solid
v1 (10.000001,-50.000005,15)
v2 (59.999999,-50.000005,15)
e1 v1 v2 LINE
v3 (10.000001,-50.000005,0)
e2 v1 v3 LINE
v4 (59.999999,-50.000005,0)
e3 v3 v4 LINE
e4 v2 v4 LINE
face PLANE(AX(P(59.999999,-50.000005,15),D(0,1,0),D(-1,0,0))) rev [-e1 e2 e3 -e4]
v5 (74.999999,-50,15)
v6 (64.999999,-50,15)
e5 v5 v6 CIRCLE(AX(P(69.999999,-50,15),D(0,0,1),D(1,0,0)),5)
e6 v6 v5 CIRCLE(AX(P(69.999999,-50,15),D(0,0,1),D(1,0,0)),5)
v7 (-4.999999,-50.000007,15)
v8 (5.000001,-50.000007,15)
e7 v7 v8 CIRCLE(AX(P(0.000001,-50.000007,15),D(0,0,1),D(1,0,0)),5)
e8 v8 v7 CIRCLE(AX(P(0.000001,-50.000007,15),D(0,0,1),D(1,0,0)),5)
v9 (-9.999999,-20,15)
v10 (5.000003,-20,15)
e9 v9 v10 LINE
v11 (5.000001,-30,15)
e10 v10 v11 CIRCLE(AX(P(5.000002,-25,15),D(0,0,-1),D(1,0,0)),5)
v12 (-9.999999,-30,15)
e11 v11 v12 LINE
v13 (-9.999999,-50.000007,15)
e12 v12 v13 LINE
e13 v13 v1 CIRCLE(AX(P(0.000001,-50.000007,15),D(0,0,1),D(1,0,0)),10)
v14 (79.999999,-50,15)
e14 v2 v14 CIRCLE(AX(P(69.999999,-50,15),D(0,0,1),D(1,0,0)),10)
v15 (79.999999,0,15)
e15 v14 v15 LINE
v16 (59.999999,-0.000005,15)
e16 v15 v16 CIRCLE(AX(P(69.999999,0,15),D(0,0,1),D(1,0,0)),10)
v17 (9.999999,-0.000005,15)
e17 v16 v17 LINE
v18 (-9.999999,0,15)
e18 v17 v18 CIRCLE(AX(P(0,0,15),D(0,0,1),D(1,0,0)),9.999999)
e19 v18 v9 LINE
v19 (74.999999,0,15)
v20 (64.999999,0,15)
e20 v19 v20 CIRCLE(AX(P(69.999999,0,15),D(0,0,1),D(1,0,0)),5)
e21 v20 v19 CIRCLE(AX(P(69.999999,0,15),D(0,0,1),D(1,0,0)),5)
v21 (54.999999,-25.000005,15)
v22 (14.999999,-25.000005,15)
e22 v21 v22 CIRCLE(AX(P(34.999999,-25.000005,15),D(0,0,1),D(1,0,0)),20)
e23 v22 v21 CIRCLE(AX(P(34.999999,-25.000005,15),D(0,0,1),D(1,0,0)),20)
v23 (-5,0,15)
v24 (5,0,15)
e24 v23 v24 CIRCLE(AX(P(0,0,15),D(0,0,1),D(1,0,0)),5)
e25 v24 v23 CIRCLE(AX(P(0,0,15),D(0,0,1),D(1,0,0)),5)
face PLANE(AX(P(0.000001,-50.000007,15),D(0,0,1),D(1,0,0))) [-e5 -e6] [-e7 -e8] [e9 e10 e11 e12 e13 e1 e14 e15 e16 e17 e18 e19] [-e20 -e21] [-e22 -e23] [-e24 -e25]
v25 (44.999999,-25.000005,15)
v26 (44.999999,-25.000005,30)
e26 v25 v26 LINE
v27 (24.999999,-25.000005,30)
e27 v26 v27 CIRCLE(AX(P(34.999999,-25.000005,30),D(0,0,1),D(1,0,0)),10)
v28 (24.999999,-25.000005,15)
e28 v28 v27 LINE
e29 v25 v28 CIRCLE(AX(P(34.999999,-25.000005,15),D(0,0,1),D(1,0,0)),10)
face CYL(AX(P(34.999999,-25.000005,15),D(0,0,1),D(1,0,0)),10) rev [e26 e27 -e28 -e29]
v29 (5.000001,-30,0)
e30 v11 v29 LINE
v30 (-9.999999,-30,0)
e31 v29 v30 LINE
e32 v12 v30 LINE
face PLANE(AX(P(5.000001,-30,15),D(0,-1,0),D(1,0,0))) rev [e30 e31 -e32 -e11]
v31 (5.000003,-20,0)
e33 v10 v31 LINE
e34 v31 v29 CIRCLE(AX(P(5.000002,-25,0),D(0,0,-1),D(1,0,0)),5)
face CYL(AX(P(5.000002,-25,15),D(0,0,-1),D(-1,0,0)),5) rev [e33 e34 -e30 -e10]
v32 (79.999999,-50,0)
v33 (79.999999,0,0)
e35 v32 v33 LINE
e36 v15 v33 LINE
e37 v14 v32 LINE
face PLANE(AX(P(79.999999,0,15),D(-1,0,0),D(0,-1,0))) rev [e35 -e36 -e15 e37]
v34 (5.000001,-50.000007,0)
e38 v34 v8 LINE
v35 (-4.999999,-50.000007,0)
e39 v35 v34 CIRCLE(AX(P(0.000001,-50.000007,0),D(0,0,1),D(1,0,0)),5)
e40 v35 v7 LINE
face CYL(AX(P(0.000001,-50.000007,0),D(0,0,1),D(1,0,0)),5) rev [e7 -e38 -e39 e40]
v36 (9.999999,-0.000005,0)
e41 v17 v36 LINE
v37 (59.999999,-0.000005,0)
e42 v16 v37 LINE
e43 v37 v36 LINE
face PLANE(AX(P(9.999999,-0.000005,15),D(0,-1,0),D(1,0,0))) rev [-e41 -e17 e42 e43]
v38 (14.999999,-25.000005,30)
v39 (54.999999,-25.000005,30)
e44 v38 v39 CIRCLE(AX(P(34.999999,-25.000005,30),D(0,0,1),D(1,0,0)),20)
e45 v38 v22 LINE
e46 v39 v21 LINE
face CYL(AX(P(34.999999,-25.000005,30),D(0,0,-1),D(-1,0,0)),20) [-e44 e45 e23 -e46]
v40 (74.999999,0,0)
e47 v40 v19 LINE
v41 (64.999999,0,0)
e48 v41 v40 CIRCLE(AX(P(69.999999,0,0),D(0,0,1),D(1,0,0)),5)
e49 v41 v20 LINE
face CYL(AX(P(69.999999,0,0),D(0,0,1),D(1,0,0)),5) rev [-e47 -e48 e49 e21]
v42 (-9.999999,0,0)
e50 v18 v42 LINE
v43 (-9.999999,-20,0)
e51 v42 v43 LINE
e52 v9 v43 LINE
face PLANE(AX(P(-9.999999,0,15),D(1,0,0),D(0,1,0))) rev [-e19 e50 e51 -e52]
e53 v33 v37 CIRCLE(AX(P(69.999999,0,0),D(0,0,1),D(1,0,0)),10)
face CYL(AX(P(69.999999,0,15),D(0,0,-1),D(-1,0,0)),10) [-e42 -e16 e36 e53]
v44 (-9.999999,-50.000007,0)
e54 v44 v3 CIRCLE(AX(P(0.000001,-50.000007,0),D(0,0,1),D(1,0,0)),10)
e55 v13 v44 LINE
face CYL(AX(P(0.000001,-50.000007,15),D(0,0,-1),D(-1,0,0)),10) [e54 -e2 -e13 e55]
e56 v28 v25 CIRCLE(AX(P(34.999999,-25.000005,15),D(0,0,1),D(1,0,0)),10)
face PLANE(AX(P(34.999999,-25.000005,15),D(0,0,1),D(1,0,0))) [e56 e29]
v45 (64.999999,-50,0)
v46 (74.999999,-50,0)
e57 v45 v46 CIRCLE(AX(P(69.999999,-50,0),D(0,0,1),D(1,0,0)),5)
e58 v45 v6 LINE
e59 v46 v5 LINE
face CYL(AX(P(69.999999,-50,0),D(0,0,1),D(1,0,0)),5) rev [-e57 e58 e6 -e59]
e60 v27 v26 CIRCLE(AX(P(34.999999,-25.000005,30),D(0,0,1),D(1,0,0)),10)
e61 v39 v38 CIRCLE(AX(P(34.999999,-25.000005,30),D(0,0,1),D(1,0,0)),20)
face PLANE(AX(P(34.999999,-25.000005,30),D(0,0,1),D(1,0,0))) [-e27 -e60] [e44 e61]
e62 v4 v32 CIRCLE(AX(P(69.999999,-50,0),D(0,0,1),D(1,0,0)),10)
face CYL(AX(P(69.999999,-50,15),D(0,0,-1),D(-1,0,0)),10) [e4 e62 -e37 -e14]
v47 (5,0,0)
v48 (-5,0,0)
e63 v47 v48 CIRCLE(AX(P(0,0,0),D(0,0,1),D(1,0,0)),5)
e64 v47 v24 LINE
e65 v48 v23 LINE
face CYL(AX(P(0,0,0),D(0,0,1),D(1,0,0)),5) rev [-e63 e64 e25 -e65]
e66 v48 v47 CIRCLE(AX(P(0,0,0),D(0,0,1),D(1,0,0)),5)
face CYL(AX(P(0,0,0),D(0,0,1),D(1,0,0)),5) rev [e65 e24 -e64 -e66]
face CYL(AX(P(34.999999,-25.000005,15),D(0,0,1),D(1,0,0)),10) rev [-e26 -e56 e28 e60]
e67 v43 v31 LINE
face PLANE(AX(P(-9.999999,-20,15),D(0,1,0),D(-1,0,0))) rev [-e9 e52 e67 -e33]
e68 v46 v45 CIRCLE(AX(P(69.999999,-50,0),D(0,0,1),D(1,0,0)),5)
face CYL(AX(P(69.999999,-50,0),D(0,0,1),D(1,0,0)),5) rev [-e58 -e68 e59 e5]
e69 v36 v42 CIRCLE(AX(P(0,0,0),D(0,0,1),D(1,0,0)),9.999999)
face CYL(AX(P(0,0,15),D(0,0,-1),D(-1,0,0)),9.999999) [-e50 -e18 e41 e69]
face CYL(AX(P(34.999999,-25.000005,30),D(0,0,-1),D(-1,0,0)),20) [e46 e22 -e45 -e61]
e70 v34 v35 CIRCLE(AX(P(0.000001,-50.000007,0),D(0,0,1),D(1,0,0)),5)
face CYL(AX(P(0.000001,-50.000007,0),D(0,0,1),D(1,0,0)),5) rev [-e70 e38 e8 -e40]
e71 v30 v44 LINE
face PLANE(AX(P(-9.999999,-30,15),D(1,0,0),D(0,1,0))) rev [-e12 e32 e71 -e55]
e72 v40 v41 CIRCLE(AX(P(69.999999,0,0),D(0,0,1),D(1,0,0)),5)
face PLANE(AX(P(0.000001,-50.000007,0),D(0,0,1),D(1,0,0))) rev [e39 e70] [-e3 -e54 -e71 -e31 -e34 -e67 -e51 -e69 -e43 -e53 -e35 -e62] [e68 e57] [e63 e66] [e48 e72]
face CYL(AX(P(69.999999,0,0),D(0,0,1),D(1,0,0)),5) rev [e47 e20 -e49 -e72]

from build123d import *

# Parameters (mm, degrees)
FLANGE_PLATE_DEPTH     = 15
SIDE_NOTCH_SKETCH_R    = 5
SIDE_NOTCH_10X10_DEPTH = 15
HUB_BOSS_SKETCH_R      = 20
HUB_BOSS_40_DEPTH      = 15
BORE_SKETCH_R          = 10
BORE_20_DEPTH          = 15


with BuildPart() as part:
    # Flange Plate Profile Sketch → Flange Plate (new body)
    with BuildSketch(Plane.XY):
        with BuildLine():
            Line((9.999999107, -5.133e-06), (59.999999107, -5.133e-06))
            ThreePointArc((59.999999107, -5.133e-06), (69.999996541, 10), (79.999999107, 0))
            Line((79.999999107, 0), (79.999999107, -50))
            ThreePointArc((79.999999107, -50), (70.000001674, -60), (59.999999107, -50.000005133))
            Line((59.999999107, -50.000005133), (10.000000893, -50.000005133))
            ThreePointArc((10.000000893, -50.000005133), (1.674e-06, -60.000006696), (-9.999999107, -50.000006696))
            Line((-9.999999107, -50.000006696), (-9.999999107, -30))
            Line((-9.999999107, -30), (5.000000893, -30))
            ThreePointArc((5.000000893, -30), (10.000001691, -25.000000893), (5.000002678, -20))
            Line((5.000002678, -20), (-9.999999107, -20))
            Line((-9.999999107, -20), (-9.999999107, 0))
            ThreePointArc((-9.999999107, 0), (2.567e-06, 9.999999107), (9.999999107, -5.133e-06))
        make_face()
    extrude(amount=FLANGE_PLATE_DEPTH)

    # Side Notch Sketch → Side Notch 10x10 (cut)
    with BuildSketch(Plane.XY.offset(15)):
        Circle(SIDE_NOTCH_SKETCH_R)
        with Locations((69.999999107, 0)):
            Circle(SIDE_NOTCH_SKETCH_R)
        with Locations((69.999999107, -50)):
            Circle(SIDE_NOTCH_SKETCH_R)
        with Locations((8.93e-07, -50.000006696)):
            Circle(SIDE_NOTCH_SKETCH_R)
    extrude(amount=-SIDE_NOTCH_10X10_DEPTH, mode=Mode.SUBTRACT)

    # Hub Boss Sketch → Hub Boss Ø40 (add)
    with BuildSketch(Plane.XY.offset(15)):
        with Locations((34.999999107, -25.000005133)):
            Circle(HUB_BOSS_SKETCH_R)
    extrude(amount=HUB_BOSS_40_DEPTH)

    # Bore Sketch → Bore Ø20 (cut)
    with BuildSketch(Plane.XY.offset(30)):
        with Locations((34.999999107, -25.000005133)):
            Circle(BORE_SKETCH_R)
    extrude(amount=-BORE_20_DEPTH, mode=Mode.SUBTRACT)


solid = part.part
